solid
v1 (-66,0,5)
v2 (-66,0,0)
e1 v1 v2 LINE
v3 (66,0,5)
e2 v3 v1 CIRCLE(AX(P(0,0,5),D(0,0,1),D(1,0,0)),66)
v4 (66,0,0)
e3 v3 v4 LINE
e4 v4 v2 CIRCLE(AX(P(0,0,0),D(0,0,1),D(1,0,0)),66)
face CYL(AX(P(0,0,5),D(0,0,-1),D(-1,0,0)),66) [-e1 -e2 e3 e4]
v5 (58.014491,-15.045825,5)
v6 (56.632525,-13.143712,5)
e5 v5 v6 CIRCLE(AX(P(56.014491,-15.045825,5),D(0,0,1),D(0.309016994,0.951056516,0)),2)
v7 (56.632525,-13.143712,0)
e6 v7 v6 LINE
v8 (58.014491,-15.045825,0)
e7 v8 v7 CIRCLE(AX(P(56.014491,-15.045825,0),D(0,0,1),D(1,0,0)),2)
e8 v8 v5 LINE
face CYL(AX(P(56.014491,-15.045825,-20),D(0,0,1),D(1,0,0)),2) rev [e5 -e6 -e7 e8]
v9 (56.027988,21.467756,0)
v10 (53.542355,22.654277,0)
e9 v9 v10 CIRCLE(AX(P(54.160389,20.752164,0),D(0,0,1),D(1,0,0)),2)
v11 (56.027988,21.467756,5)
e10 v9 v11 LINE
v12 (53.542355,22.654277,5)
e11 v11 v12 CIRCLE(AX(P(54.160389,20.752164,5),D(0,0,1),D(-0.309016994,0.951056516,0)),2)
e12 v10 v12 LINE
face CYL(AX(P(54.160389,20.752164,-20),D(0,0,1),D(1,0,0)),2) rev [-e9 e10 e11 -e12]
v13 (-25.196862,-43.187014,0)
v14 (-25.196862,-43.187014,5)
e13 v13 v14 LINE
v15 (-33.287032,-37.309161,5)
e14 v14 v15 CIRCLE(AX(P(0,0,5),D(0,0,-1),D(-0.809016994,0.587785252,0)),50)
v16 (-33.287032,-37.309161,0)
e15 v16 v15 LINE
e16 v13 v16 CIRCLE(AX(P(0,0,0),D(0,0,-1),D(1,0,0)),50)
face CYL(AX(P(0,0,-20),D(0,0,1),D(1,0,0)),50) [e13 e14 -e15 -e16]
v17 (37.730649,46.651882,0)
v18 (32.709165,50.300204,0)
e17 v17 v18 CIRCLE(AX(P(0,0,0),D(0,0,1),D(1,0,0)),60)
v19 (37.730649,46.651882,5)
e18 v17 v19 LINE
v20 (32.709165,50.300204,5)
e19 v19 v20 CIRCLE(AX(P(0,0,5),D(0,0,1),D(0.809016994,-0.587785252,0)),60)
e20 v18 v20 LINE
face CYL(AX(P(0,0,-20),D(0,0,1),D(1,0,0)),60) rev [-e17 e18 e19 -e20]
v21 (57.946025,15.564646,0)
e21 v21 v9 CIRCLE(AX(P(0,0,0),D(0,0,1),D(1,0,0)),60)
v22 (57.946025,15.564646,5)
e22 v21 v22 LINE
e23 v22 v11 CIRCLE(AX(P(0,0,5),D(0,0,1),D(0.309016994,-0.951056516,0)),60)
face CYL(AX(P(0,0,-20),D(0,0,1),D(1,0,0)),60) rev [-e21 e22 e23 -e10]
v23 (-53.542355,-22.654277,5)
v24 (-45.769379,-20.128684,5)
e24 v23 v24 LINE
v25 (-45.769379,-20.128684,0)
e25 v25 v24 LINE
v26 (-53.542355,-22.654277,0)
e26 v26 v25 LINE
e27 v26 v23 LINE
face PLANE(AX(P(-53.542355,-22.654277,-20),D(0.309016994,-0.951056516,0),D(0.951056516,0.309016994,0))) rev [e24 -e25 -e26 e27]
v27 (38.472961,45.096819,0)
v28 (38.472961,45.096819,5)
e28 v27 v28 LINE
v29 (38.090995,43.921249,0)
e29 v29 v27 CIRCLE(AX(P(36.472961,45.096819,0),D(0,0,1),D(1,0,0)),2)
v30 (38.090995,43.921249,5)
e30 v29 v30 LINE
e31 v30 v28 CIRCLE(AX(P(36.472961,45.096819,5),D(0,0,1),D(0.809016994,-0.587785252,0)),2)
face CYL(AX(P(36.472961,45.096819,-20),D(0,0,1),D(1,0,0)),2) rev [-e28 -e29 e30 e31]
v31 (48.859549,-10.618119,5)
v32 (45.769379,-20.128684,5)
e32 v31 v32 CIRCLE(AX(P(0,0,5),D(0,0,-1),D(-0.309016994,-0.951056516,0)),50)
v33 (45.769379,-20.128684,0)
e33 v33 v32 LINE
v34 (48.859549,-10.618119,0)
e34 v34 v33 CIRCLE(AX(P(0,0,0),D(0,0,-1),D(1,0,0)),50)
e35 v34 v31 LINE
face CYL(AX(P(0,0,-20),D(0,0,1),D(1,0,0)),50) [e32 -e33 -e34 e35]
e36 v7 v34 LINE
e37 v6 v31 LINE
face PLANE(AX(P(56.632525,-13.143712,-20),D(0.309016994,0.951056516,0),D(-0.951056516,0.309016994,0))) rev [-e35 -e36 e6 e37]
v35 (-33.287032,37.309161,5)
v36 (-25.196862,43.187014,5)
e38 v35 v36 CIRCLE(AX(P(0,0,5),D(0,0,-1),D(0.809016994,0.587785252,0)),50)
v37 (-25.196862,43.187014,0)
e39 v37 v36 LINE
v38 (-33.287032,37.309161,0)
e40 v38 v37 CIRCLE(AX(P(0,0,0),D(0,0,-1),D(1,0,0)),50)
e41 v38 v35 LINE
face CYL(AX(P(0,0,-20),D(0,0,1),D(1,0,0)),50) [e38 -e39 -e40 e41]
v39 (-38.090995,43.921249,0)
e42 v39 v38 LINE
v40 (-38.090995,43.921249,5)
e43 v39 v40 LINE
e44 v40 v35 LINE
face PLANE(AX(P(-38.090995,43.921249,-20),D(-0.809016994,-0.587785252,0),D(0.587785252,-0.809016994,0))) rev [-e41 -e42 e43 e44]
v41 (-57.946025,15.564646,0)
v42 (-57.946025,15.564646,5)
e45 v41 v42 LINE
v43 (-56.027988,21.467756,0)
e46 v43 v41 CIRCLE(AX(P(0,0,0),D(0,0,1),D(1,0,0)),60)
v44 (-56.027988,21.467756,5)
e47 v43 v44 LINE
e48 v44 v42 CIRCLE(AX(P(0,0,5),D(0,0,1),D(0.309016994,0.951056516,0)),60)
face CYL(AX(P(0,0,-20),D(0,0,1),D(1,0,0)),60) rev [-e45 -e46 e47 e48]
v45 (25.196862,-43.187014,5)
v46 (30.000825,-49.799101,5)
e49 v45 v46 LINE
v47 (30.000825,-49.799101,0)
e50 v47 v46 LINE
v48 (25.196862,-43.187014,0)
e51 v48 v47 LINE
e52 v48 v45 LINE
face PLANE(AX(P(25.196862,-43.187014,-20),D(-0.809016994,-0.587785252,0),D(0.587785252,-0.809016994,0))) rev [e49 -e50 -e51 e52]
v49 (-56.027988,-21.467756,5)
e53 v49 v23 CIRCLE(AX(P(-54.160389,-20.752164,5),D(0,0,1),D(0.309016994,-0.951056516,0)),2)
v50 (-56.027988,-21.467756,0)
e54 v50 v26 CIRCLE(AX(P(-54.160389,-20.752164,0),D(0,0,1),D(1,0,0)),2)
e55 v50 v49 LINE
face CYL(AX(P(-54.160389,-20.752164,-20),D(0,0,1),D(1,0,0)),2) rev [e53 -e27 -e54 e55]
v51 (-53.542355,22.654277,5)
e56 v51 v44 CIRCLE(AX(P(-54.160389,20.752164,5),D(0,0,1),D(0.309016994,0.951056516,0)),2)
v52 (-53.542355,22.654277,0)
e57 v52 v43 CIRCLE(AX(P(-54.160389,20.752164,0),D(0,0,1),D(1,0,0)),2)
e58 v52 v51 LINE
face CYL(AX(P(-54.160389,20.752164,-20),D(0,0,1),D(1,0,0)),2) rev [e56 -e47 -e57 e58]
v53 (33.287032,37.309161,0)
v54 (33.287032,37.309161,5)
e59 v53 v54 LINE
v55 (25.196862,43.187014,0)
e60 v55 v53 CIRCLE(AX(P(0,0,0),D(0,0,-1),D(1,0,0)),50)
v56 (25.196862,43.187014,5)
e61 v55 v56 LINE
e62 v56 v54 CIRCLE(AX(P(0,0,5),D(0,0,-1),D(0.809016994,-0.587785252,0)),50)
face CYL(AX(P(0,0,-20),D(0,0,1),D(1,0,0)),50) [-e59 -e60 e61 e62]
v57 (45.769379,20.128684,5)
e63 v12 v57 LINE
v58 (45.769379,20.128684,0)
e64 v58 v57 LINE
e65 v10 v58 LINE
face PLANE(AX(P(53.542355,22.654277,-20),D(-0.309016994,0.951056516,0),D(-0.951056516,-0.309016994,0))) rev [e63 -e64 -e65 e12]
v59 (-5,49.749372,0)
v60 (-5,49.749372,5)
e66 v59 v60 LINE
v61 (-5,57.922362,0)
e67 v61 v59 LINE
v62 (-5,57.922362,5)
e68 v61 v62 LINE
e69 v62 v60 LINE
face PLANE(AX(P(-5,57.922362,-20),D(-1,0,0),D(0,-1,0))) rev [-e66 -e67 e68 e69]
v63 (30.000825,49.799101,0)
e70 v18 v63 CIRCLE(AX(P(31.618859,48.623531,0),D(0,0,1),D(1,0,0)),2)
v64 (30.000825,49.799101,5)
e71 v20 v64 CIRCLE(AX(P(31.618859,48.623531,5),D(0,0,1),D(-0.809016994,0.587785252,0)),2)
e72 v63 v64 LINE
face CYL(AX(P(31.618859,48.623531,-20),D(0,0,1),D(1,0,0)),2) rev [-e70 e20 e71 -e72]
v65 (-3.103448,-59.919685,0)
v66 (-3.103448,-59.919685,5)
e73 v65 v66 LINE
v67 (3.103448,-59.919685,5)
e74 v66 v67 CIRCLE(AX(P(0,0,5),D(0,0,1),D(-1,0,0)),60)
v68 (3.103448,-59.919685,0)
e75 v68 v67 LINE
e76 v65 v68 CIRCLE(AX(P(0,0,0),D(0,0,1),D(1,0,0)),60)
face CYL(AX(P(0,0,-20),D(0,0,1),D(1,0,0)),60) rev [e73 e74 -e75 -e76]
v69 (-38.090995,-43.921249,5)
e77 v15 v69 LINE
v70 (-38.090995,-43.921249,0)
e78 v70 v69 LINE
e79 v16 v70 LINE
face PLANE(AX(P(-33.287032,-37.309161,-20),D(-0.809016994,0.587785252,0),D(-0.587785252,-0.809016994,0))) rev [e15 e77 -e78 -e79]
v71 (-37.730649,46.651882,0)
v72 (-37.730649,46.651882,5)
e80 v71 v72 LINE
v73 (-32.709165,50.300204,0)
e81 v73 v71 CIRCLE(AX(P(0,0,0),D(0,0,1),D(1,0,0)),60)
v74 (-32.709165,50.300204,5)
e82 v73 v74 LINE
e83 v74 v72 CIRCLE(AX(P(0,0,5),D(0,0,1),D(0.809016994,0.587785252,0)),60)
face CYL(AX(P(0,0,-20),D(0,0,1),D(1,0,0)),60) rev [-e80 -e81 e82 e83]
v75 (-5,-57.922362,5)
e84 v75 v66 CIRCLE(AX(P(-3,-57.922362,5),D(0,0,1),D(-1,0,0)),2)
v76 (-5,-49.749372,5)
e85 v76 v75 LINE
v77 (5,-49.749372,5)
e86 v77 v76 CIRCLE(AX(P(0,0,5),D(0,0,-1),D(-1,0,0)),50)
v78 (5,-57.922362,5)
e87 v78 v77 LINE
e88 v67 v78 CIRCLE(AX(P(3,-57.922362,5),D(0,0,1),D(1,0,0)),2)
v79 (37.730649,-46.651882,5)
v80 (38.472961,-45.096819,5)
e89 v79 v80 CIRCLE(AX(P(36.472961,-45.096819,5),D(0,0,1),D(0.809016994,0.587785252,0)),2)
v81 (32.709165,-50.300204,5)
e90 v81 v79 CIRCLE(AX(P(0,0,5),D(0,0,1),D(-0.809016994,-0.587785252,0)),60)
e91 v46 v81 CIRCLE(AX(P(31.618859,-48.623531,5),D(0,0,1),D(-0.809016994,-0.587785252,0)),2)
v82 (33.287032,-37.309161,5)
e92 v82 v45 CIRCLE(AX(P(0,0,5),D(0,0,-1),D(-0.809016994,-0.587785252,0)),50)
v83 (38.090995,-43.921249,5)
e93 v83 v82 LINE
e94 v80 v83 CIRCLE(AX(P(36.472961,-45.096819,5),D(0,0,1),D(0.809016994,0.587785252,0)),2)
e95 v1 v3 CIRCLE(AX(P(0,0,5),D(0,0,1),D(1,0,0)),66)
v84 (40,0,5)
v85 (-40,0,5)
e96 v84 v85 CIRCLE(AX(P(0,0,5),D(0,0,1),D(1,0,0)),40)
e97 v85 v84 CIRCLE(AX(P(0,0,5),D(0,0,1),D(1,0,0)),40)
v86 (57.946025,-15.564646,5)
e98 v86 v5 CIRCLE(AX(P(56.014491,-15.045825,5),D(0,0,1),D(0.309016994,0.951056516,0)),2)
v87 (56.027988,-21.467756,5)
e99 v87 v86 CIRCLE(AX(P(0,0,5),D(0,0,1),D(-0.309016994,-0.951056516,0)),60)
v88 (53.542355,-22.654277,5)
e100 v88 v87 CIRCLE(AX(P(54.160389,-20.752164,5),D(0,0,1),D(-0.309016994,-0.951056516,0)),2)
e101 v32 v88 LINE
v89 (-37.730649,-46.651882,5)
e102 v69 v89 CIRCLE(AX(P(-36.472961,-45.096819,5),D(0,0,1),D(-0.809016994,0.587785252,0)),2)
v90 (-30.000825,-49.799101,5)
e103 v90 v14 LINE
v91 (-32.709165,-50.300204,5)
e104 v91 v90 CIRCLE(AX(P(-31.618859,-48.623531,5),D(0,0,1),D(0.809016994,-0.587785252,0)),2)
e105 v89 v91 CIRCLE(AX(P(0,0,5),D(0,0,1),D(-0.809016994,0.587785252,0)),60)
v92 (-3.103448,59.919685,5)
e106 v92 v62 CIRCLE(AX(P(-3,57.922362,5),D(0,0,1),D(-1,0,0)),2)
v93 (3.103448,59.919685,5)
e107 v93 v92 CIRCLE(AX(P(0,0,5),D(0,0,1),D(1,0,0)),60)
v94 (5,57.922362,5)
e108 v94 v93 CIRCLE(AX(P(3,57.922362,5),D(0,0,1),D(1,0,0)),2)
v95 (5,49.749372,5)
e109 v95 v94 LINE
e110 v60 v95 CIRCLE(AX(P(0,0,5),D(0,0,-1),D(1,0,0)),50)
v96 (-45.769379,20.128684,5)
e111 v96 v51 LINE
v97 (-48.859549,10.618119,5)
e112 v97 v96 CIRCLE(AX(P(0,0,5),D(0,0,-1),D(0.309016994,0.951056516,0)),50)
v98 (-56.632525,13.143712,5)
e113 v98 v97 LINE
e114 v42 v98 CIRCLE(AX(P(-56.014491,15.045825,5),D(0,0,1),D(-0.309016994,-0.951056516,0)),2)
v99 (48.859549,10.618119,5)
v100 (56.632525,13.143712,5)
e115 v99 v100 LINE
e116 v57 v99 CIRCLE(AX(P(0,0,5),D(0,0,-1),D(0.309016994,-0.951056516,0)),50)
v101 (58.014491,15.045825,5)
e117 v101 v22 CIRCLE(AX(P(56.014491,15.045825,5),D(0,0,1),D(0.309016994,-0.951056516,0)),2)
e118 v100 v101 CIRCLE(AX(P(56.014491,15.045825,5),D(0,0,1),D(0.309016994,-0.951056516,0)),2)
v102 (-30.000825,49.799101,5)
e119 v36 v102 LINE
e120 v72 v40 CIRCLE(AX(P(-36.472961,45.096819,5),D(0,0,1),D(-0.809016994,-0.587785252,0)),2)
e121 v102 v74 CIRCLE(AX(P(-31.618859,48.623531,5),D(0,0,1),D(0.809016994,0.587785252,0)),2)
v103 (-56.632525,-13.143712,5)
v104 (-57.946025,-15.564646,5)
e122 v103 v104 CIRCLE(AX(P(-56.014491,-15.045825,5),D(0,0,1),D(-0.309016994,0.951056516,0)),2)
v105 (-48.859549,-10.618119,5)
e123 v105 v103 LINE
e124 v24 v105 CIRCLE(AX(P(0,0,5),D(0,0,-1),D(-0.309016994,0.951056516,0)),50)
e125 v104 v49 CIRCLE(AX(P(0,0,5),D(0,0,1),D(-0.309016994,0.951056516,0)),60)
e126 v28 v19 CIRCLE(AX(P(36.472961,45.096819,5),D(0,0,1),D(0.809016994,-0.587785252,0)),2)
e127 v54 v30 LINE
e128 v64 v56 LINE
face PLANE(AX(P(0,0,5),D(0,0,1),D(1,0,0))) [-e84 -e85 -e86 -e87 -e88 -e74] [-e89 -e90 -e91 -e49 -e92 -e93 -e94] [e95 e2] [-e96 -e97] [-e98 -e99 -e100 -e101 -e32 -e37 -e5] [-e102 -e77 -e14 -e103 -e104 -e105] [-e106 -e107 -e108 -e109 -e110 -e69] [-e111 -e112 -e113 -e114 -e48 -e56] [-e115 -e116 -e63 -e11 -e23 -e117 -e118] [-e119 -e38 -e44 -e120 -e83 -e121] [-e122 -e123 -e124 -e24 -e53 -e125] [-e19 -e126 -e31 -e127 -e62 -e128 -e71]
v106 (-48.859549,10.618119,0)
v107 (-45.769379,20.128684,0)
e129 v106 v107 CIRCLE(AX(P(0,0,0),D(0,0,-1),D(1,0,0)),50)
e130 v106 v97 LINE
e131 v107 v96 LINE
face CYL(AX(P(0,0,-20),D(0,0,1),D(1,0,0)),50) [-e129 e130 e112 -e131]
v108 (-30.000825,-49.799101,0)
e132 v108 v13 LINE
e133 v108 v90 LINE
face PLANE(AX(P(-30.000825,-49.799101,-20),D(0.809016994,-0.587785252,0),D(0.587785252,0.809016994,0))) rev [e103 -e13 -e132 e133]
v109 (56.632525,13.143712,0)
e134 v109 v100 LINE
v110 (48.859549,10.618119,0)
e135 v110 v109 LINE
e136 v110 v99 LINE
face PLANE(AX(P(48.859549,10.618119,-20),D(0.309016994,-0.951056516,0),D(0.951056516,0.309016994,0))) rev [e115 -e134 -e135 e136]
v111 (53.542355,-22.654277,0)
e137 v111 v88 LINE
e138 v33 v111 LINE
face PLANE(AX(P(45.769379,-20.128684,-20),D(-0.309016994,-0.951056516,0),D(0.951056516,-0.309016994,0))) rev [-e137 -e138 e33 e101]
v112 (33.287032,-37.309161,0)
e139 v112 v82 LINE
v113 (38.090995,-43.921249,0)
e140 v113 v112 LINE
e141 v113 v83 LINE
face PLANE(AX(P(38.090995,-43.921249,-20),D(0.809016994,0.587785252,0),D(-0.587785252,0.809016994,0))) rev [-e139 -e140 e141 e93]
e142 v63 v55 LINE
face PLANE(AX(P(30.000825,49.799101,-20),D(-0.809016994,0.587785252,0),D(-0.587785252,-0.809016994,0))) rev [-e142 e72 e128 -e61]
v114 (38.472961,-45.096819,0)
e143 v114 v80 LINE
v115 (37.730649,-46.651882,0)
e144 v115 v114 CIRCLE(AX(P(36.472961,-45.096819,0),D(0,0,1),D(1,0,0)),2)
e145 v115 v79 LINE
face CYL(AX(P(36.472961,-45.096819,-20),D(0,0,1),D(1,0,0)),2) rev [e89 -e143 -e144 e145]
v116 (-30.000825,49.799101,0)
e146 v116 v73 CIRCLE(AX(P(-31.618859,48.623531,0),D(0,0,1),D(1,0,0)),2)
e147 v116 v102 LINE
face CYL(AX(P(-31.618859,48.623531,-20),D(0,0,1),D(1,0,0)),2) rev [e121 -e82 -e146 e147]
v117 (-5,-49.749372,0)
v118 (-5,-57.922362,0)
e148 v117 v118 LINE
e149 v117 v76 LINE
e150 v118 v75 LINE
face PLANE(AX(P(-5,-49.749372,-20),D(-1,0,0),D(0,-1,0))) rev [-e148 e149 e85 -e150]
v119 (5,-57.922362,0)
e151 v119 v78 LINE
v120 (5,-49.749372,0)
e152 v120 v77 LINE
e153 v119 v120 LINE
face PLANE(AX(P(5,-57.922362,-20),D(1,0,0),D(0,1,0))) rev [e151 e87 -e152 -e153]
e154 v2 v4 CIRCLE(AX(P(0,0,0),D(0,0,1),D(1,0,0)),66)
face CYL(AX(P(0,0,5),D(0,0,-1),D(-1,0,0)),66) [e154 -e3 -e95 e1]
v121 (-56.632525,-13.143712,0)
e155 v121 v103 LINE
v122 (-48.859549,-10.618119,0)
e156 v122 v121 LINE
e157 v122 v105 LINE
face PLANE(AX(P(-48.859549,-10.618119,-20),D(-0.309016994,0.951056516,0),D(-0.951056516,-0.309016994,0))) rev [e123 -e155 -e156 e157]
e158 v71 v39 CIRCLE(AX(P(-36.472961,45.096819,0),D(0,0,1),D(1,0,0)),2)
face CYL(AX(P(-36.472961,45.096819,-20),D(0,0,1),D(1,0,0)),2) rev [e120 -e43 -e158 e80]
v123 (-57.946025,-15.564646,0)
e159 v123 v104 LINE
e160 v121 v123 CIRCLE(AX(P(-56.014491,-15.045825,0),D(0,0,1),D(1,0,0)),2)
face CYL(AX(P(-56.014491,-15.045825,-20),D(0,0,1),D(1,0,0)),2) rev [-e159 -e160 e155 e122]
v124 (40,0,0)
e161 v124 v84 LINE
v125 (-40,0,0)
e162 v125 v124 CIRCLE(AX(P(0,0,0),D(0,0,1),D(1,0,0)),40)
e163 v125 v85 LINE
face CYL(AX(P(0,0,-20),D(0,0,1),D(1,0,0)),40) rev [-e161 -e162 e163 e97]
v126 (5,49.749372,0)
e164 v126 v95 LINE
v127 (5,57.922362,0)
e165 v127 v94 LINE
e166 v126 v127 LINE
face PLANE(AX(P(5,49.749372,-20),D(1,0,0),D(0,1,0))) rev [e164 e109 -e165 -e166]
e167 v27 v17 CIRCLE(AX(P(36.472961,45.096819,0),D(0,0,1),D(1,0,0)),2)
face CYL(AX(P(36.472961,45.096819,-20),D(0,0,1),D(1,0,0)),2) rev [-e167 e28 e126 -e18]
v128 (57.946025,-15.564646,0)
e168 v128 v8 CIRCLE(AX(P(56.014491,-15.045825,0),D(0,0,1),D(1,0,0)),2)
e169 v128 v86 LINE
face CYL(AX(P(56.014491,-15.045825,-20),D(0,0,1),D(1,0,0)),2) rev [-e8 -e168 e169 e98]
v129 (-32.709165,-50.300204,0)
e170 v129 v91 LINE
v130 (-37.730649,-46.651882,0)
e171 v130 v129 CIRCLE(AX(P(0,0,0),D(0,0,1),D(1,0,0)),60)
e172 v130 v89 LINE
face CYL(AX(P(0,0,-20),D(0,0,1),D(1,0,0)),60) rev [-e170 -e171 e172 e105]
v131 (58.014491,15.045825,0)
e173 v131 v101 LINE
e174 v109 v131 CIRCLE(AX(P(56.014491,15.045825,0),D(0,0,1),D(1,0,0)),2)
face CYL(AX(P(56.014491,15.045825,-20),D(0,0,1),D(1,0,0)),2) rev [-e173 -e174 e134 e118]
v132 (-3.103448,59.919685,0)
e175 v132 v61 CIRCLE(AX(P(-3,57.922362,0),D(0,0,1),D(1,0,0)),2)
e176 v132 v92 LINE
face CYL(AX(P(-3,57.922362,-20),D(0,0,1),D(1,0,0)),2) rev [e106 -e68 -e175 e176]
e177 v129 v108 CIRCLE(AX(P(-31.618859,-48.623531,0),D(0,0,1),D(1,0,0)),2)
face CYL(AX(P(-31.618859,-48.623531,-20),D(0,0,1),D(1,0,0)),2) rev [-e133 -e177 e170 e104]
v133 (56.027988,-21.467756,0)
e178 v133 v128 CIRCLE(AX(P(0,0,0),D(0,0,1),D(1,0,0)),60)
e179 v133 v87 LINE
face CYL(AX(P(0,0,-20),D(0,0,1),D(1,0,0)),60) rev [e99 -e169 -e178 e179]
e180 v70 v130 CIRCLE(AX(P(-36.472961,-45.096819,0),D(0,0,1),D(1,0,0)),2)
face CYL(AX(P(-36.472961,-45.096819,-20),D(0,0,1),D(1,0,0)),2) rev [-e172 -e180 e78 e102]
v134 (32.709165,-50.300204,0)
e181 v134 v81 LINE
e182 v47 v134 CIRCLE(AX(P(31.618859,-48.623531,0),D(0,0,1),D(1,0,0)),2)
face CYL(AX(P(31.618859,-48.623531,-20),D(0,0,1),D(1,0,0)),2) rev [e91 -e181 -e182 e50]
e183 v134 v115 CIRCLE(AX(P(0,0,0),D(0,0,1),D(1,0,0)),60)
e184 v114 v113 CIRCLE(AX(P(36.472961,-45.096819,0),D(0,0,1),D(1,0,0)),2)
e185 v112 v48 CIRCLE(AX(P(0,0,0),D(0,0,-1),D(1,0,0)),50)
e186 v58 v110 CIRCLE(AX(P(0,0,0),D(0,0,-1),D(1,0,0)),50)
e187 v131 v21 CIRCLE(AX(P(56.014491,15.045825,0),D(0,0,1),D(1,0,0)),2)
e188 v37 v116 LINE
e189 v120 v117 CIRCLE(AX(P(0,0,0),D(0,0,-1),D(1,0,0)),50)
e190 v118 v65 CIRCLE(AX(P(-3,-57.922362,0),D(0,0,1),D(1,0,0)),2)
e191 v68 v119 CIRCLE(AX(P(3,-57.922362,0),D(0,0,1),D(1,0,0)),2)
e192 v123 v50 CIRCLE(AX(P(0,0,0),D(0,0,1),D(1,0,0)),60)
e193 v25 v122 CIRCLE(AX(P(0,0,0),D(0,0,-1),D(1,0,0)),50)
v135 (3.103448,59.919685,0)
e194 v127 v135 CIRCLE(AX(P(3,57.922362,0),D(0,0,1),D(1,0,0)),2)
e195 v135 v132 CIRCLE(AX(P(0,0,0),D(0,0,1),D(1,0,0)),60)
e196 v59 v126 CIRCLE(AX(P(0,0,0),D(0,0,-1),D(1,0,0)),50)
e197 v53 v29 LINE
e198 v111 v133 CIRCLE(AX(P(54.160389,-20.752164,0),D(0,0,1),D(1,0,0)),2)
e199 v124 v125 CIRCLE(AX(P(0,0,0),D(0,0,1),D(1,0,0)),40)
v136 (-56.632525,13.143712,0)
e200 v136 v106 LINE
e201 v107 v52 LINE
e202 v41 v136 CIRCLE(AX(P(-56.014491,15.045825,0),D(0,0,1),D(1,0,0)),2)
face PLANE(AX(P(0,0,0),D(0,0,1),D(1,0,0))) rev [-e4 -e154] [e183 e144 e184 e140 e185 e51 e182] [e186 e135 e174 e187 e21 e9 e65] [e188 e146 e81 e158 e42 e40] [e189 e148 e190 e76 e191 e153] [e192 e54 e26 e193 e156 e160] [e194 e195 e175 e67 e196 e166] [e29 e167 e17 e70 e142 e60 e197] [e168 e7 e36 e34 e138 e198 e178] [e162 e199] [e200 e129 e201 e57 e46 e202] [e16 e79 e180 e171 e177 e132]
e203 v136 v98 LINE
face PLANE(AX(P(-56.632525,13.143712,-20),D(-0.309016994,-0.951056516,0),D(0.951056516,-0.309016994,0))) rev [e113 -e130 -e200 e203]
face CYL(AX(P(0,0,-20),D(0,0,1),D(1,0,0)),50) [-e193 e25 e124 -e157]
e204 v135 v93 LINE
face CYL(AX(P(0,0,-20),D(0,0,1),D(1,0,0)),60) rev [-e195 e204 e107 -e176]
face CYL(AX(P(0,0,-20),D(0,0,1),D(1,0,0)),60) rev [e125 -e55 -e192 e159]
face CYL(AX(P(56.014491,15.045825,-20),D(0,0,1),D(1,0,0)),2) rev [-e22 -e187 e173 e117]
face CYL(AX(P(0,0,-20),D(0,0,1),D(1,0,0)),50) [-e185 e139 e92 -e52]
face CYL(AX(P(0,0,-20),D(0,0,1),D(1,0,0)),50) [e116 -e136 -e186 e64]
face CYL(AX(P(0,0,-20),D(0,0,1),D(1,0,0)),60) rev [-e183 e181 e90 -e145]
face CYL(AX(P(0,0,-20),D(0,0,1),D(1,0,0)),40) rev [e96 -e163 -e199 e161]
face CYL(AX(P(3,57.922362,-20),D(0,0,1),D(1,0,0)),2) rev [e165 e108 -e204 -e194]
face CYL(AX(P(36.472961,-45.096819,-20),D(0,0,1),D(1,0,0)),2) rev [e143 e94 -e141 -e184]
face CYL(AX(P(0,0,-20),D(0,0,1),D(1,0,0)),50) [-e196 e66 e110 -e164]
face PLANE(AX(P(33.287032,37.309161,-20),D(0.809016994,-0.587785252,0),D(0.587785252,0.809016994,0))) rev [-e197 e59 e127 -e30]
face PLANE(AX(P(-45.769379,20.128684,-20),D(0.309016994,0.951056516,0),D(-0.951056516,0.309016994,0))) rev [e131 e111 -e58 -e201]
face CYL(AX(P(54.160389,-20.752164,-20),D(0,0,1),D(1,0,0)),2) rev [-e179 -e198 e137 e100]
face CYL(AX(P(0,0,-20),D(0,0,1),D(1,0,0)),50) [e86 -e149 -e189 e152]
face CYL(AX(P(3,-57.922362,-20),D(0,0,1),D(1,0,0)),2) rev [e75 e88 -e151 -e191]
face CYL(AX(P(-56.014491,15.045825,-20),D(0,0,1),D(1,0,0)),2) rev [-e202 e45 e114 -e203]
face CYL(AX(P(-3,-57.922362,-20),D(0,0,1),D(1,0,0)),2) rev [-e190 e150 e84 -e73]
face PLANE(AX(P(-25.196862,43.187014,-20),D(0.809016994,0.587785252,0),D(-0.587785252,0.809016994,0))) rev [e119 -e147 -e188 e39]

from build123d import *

# Parameters (mm, degrees)
RING_OUTLINE_SKETCH_132_R = 66
RING_DISC_132X5_DEPTH     = 5
WINDOW_CUT_DEPTH          = 25
WINDOW_PATTERN_10X_COUNT  = 10
BORE_SKETCH_80_R          = 40
CENTRE_BORE_80_DEPTH      = 25


with BuildPart() as part:
    # Ring Outline Sketch Ø132 → Ring Disc Ø132x5 (new body)
    with BuildSketch(Plane.XY):
        Circle(RING_OUTLINE_SKETCH_132_R)
    extrude(amount=RING_DISC_132X5_DEPTH)

    # Window Sketch → Window Cut (cut)
    with BuildSketch(Plane.XY.offset(5)):
        with BuildLine():
            Line((5, 49.749371855), (5, 57.92236183))
            ThreePointArc((5, 57.92236183), (4.450326955, 59.299515316), (3.103448276, 59.919684652))
            ThreePointArc((3.103448276, 59.919684652), (0, 60), (-3.103448276, 59.919684652))
            ThreePointArc((-3.103448276, 59.919684652), (-4.450326955, 59.299515316), (-5, 57.92236183))
            Line((-5, 57.92236183), (-5, 49.749371855))
            ThreePointArc((-5, 49.749371855), (0, 50), (5, 49.749371855))
        make_face()
    window_cut = extrude(amount=-WINDOW_CUT_DEPTH, mode=Mode.SUBTRACT)

    # Window Pattern 10x: Window Cut ×10 about axis
    window_pattern_10x_axis = Axis((0, 0, 0), (0, 0, 1))
    for i in range(1, WINDOW_PATTERN_10X_COUNT):
        add(window_cut.rotate(window_pattern_10x_axis, i * 360 / WINDOW_PATTERN_10X_COUNT), mode=Mode.SUBTRACT)

    # Bore Sketch Ø80 → Centre Bore Ø80 (cut)
    with BuildSketch(Plane.XY.offset(5)):
        Circle(BORE_SKETCH_80_R)
    extrude(amount=-CENTRE_BORE_80_DEPTH, mode=Mode.SUBTRACT)


solid = part.part
